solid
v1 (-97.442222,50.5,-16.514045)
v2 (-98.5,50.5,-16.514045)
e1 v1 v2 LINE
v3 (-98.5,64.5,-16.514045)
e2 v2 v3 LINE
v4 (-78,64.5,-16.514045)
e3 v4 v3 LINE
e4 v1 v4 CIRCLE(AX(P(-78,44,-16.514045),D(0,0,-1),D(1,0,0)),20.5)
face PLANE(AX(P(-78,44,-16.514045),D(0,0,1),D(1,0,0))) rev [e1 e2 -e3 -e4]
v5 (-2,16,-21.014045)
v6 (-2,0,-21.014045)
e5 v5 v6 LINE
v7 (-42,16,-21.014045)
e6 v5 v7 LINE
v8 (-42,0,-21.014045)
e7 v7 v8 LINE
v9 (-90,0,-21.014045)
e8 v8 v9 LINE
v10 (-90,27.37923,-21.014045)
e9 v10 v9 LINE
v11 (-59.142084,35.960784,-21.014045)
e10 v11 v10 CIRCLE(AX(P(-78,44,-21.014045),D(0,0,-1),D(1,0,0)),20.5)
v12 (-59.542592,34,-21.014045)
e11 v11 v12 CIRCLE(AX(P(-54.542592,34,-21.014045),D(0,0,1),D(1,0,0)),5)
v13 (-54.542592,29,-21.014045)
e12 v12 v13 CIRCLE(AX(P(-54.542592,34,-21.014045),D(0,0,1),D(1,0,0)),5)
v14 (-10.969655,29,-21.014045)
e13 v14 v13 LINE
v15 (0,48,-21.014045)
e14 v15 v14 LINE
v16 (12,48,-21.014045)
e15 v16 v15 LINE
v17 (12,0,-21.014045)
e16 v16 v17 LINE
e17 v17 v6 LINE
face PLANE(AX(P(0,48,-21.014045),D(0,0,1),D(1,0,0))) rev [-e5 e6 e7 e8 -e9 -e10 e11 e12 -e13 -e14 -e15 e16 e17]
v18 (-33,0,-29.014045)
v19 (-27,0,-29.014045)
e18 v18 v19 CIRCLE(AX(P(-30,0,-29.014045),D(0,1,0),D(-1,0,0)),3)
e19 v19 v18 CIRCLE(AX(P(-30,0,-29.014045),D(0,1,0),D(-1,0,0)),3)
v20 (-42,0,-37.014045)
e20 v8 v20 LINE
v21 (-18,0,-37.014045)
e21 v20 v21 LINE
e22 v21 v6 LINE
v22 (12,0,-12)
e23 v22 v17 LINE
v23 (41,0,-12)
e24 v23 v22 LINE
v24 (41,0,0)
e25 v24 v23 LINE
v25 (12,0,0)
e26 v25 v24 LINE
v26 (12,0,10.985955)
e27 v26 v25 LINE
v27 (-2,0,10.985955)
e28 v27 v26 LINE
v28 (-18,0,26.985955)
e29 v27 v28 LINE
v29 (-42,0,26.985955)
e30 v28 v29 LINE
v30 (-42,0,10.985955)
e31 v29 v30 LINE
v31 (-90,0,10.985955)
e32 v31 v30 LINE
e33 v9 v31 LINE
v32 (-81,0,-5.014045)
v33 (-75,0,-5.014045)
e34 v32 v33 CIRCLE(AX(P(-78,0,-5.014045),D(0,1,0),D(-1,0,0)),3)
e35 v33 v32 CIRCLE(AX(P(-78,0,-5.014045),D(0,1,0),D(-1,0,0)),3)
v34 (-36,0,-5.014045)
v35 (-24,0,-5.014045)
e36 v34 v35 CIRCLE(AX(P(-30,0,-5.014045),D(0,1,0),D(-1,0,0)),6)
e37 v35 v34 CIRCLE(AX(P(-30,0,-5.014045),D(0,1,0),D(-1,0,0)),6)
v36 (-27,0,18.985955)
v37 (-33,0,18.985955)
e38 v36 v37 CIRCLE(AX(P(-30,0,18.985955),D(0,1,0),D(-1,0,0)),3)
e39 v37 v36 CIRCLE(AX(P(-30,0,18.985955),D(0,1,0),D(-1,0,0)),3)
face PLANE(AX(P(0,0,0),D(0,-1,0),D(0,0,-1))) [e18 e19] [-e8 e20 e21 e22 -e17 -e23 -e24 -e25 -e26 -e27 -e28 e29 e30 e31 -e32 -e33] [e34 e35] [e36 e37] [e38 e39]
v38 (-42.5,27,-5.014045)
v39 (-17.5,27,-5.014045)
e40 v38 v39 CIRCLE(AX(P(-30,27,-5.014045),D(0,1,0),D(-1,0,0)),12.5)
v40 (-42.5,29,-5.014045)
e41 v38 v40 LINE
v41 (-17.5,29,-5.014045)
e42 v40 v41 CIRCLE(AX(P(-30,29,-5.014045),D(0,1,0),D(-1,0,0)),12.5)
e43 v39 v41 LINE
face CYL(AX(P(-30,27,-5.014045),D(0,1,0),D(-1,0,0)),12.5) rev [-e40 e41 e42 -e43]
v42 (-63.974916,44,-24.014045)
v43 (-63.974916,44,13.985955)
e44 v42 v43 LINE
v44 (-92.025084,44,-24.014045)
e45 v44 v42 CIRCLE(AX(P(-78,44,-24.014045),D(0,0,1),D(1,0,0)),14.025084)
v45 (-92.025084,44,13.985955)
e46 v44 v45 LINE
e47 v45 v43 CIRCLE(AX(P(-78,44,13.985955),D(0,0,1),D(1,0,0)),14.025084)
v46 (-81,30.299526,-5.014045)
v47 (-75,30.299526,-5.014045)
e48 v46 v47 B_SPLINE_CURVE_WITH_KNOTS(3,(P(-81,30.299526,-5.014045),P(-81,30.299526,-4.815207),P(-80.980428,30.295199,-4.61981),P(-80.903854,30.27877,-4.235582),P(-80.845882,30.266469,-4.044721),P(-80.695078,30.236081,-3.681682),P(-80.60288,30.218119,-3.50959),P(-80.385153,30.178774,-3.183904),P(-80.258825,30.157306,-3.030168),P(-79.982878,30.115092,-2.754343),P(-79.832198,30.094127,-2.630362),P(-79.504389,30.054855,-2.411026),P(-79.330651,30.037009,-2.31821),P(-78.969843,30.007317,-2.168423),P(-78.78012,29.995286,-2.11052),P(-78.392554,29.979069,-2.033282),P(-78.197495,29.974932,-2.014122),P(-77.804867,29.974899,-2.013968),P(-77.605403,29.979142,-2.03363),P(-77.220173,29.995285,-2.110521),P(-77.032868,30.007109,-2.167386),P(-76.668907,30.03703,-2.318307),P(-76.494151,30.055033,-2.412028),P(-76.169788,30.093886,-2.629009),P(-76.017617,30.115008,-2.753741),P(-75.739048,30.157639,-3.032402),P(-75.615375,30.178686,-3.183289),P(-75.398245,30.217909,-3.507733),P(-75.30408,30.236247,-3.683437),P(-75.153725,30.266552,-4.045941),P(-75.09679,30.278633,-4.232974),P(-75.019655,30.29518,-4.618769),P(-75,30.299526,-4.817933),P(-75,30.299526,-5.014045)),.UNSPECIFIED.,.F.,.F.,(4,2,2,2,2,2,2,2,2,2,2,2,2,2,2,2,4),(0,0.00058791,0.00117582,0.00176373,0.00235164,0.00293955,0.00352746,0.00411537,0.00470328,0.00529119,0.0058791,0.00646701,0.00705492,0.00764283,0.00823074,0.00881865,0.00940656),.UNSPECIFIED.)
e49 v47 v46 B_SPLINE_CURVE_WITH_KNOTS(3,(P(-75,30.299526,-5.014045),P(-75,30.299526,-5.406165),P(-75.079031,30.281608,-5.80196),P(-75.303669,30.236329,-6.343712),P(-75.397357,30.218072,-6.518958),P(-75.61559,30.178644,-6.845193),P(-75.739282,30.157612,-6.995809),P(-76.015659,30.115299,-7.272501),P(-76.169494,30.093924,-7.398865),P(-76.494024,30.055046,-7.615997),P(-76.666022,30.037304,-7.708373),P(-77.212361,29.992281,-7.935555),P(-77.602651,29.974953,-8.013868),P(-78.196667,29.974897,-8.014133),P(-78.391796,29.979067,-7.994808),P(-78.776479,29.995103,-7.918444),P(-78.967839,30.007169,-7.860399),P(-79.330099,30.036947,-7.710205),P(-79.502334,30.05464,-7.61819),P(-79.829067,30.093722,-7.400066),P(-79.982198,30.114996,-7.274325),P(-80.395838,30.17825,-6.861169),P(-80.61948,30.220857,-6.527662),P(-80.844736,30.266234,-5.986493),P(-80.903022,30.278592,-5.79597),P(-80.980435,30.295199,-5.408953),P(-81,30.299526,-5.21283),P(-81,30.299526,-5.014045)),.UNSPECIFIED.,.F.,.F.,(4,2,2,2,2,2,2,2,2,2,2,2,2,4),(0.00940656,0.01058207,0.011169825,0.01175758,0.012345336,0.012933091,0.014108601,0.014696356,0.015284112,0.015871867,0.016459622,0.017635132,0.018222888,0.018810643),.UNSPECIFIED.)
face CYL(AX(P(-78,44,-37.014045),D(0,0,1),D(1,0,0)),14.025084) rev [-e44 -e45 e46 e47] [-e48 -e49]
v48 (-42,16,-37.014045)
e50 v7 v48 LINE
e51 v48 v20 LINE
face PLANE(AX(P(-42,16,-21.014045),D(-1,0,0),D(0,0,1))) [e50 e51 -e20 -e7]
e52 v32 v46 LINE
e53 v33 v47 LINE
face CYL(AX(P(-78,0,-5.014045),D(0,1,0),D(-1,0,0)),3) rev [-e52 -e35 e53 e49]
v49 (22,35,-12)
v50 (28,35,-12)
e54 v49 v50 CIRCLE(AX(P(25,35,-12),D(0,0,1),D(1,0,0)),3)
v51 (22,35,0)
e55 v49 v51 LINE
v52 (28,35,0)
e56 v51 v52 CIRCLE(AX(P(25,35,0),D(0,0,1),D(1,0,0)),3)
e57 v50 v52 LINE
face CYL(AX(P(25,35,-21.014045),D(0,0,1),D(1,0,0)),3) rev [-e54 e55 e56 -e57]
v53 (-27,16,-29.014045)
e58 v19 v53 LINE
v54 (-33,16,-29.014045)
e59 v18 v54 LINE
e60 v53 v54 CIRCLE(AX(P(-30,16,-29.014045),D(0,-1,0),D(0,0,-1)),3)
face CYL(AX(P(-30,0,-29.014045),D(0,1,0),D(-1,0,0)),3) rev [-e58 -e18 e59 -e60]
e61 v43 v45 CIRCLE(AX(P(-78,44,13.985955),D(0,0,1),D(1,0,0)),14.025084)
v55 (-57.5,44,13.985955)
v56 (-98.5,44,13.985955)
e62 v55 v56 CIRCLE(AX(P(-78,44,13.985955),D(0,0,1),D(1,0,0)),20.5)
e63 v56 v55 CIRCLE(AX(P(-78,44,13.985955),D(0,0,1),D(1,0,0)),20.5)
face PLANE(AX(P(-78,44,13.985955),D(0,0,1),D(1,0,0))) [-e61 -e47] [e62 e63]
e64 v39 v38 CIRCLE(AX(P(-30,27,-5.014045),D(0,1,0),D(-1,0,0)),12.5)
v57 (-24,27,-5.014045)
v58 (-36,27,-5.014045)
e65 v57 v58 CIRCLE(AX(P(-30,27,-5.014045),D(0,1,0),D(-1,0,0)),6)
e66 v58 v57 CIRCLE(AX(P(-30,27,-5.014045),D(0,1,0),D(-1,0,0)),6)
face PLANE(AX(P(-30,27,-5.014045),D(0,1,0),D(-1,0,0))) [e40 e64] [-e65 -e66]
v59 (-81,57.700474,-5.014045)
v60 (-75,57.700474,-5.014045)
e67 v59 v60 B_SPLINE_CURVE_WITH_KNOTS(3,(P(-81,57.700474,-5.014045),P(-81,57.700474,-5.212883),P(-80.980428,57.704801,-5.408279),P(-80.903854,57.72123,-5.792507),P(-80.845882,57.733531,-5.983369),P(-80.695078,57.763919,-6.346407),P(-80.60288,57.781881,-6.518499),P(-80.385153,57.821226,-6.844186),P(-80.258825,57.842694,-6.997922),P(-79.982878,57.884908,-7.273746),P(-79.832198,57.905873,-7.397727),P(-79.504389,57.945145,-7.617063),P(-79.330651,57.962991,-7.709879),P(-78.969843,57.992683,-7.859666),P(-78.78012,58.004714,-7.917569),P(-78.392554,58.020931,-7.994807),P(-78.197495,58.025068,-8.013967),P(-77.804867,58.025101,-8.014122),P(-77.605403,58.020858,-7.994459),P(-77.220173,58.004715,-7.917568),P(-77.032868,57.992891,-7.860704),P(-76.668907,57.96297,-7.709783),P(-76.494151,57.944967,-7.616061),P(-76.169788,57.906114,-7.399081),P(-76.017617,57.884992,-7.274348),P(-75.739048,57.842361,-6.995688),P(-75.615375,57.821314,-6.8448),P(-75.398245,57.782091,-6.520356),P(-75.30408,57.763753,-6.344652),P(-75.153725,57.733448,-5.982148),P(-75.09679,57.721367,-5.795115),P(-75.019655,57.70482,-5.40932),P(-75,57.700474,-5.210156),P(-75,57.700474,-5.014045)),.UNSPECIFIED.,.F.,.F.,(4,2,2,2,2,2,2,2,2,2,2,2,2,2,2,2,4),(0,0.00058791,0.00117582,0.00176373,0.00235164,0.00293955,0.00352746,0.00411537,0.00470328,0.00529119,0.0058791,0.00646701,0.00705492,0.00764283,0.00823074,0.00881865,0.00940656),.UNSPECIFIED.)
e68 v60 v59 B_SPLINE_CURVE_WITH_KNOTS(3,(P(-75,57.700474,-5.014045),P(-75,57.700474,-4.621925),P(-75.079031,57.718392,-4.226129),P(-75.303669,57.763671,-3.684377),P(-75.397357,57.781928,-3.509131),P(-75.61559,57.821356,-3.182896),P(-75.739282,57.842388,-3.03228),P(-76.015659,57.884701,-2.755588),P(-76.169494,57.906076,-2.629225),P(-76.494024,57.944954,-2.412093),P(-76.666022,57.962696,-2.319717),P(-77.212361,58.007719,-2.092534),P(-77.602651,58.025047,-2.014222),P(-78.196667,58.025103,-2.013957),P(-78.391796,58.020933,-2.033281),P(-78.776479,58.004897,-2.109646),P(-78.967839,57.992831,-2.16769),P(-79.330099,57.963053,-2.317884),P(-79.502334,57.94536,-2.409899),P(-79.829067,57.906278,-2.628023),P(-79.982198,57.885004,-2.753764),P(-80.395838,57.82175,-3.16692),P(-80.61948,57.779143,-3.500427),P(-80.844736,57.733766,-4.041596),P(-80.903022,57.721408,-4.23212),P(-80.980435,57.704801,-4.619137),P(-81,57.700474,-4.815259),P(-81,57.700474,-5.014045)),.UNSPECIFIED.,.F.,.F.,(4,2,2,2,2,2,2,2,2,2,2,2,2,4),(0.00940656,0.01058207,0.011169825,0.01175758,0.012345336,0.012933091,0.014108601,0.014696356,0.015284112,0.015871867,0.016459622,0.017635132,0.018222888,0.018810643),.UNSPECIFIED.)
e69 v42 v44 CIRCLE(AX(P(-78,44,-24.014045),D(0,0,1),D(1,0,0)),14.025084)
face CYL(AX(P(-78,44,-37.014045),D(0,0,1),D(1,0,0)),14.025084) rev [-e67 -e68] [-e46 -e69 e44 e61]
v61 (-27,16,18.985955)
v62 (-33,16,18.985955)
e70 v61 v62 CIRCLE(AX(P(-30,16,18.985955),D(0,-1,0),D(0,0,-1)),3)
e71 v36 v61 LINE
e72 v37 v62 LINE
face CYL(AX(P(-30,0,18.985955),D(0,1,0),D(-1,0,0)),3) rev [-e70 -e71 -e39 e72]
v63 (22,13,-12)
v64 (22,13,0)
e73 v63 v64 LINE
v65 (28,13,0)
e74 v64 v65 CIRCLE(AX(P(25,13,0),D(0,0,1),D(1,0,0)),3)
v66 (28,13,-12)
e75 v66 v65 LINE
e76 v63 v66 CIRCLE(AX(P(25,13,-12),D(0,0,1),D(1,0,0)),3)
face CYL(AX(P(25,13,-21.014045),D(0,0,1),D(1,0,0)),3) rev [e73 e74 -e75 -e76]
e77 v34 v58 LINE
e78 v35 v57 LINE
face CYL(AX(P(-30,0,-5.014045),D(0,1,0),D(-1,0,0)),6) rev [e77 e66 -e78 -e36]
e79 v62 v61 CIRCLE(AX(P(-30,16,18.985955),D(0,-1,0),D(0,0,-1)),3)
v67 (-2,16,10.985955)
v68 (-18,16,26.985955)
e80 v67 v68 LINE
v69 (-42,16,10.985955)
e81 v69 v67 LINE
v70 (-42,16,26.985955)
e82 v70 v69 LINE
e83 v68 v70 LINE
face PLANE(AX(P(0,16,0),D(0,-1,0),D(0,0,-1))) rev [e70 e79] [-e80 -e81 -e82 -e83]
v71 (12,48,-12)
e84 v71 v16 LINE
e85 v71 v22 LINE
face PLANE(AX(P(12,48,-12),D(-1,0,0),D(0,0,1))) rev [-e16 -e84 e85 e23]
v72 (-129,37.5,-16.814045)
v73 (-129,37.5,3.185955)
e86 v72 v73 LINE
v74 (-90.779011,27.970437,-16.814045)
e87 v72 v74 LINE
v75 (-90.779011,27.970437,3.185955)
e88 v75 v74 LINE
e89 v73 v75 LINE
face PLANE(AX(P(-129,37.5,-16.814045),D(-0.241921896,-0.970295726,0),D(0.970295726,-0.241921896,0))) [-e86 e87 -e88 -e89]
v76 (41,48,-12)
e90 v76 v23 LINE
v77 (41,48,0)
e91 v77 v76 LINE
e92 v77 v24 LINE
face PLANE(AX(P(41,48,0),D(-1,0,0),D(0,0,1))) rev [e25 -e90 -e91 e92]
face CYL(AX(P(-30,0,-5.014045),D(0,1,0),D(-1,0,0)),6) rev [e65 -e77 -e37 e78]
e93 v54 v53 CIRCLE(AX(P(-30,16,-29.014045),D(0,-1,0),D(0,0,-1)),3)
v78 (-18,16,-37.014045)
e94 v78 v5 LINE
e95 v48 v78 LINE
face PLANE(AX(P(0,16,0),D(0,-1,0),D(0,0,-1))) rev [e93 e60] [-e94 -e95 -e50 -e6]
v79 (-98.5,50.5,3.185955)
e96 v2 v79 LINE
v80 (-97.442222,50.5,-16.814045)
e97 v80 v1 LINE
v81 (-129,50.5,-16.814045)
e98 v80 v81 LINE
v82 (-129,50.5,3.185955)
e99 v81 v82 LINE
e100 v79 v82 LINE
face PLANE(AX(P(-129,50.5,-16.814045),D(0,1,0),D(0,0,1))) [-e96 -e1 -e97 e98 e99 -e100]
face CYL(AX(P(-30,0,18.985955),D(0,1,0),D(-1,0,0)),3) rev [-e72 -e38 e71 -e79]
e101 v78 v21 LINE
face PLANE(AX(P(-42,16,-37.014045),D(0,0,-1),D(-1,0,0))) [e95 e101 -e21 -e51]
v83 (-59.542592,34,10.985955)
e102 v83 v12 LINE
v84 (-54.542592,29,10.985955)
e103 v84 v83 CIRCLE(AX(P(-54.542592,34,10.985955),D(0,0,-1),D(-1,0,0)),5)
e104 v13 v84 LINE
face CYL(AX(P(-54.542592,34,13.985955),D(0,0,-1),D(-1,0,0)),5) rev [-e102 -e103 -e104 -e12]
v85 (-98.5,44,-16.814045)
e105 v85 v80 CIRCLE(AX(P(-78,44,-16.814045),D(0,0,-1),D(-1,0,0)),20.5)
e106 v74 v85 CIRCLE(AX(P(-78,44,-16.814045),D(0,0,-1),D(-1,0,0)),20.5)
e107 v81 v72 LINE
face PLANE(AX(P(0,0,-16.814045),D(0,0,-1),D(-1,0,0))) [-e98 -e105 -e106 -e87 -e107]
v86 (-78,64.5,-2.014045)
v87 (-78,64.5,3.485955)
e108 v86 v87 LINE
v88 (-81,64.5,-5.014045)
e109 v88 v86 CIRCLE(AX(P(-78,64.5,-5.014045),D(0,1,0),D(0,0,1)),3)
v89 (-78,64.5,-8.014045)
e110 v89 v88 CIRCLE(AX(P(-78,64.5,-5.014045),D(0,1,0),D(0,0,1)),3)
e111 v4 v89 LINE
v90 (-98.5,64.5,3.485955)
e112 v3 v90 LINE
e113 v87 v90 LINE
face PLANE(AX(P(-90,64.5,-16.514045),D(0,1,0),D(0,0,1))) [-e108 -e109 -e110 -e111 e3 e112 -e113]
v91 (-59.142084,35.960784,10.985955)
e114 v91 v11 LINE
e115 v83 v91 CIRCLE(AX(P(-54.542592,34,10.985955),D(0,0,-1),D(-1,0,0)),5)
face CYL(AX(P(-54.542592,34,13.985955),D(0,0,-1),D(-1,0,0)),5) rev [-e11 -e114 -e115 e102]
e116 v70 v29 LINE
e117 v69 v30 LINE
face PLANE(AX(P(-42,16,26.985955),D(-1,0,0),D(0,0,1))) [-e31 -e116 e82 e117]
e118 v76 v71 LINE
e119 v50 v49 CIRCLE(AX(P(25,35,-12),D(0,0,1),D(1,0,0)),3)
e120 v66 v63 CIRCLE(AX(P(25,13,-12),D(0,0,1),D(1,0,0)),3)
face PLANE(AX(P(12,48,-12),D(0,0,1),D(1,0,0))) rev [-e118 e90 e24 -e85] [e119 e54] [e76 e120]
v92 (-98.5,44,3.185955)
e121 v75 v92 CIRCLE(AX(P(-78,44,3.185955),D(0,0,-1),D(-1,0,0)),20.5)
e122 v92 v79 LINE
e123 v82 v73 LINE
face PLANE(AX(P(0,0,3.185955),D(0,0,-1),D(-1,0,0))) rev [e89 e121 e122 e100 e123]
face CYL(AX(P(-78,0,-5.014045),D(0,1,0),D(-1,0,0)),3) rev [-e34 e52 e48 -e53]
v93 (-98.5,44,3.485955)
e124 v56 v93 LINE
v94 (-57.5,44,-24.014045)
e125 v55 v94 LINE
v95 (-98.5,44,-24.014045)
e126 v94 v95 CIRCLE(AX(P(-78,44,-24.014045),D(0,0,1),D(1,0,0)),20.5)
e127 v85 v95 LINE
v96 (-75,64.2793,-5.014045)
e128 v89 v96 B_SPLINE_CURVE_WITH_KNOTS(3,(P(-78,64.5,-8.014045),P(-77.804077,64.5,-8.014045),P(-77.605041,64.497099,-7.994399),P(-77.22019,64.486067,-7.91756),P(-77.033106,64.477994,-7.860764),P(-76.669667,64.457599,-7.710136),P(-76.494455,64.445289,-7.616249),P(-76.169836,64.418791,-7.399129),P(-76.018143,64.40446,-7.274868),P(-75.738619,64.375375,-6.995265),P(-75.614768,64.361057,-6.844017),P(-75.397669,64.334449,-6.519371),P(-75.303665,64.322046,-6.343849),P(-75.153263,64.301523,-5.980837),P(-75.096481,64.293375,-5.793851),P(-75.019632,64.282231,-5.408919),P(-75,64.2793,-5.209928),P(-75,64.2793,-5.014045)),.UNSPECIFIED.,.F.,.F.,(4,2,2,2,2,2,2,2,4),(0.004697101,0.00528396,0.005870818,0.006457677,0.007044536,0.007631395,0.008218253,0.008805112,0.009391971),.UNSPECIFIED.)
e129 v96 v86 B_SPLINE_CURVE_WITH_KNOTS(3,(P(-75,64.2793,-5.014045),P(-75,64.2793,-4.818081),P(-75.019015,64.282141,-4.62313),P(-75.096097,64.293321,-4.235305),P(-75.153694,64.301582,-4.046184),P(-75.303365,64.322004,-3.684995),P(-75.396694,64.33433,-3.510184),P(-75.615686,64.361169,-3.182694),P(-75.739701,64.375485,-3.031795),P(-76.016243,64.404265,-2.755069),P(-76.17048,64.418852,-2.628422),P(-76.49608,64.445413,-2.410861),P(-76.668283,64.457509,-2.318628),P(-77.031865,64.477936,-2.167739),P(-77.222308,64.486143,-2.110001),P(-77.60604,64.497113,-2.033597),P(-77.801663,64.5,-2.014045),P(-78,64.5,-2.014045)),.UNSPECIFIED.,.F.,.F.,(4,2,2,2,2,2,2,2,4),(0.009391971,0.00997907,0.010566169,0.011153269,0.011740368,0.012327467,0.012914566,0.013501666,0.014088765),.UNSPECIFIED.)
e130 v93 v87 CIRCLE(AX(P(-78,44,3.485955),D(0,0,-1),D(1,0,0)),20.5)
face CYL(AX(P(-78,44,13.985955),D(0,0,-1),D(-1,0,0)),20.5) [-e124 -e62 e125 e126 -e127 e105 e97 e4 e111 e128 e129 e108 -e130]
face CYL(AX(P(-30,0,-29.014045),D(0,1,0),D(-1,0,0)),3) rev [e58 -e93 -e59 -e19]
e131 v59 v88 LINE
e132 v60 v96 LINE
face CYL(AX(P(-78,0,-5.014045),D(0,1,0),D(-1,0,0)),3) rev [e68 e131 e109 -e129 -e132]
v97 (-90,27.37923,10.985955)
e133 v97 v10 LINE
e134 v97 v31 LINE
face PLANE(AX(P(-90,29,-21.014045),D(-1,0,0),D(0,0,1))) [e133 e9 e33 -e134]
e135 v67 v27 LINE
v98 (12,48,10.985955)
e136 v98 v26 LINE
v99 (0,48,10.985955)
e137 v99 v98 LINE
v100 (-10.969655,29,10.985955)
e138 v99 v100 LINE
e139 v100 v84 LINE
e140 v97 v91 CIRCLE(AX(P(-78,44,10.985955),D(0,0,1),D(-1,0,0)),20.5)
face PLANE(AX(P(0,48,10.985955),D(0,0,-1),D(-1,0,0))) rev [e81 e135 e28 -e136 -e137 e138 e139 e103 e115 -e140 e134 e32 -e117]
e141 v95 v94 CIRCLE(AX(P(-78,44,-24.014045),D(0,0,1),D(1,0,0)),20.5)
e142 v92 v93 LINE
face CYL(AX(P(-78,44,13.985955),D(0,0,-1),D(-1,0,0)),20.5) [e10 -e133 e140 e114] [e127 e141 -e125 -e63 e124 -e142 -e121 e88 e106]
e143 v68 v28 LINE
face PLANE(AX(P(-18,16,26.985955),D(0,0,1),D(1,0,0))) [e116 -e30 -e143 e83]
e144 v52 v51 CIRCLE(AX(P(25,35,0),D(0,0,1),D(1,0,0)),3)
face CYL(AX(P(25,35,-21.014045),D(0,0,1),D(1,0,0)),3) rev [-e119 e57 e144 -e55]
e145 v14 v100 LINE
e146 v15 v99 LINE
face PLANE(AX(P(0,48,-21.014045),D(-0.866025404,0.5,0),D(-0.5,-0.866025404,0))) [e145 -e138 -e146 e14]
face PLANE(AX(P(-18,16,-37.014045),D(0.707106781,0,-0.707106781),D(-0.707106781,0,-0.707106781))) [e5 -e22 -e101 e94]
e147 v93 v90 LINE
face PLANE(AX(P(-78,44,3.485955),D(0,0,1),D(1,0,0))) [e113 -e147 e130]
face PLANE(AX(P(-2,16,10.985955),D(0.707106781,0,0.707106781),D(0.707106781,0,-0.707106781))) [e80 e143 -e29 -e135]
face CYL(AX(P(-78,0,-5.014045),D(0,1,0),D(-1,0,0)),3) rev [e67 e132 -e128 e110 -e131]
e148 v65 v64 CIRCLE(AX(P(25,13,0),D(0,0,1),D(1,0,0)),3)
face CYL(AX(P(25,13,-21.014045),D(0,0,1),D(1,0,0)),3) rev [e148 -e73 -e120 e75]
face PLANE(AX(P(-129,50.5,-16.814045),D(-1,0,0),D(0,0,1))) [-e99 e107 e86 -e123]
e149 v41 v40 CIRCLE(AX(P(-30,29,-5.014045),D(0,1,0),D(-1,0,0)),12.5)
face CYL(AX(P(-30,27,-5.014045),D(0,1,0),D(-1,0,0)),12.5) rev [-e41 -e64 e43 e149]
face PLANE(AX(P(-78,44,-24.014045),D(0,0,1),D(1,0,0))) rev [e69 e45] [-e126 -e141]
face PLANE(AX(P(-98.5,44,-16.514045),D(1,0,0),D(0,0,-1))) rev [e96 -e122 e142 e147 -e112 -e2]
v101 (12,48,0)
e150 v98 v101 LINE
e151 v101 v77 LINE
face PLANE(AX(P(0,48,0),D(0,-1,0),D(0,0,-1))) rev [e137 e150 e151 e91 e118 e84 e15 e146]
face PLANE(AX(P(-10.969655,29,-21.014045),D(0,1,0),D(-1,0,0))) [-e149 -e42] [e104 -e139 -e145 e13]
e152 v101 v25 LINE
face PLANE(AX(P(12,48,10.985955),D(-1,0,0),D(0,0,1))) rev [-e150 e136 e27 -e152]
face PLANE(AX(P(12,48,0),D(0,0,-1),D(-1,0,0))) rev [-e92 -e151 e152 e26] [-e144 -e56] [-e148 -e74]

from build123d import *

# Parameters (mm, degrees)
BASE_BLOCK_48MM_DEPTH      = 48
BASE_NOTCH_SKETCH_R        = 3
BASE_NOTCH_CUT_DEPTH       = 67.532624112
ANGLED_ARM_30DEG_DEPTH     = 32
MOUNTING_FLANGE_DEPTH      = 3
MOUNTING_FLANGE_DEPTH_BACK = 35
MOUNTING_FLANGE_SKETCH_R   = 20.5
MOUNTING_FLANGE_SKETCH_R_2 = 14
RAISED_BLOCK_16MM_DEPTH    = 16
POCKET_SKETCH_R            = 3.17708526
POCKET_SKETCH_R_2          = 3.631937334
POCKET_SKETCH_R_3          = 12.5
POCKET_CUT_2MM_DEPTH       = 2
SLOT_SKETCH_R              = 6
SLOT_SKETCH_R_2            = 3
SLOT_CUT_DEPTH             = 112.707383368
CHANNEL_CUT_DEPTH          = 112.05196756
CHANNEL_CUT_DEPTH_BACK     = 112.05196756
CHANNEL_SKETCH_R           = 3
LUG_START                  = -27.5
LUG_A_DEPTH                = 20
LUG_B_DEPTH                = 20
LUG_START_2                = -10.8
LUG_C_DEPTH                = 20
FLANGE_HOLE_DEPTH          = 153.977939634
FLANGE_HOLE_DEPTH_BACK     = 153.977939634
FLANGE_HOLE_SKETCH_R       = 14.02508448
LUG_A_HOLE_DEPTH           = 149.900266997
LUG_A_HOLE_DEPTH_BACK      = 149.900266997
LUG_A_HOLE_SKETCH_R        = 3
ARM_FILLET_R5_R            = 5


with BuildPart() as part:
    # Base Block Sketch → Base Block 48mm (new body)
    with BuildSketch(Plane(origin=(0, 0, 0), x_dir=(1, 0, 0), z_dir=(0, 1, 0))):
        Polygon((12, 0), (41, 0), (41, 12), (12, 12), (12, 21.014044617), (0, 21.014044617), (0, -10.985955383), (12, -10.985955383), align=None)
    extrude(amount=BASE_BLOCK_48MM_DEPTH)

    # Base Notch Sketch → Base Notch Cut (cut, through all)
    with BuildSketch(Plane.XY):
        with Locations((25, 35)):
            Circle(BASE_NOTCH_SKETCH_R)
        with Locations((25, 13)):
            Circle(BASE_NOTCH_SKETCH_R)
    extrude(amount=-BASE_NOTCH_CUT_DEPTH, mode=Mode.SUBTRACT)

    # Angled Arm Sketch → Angled Arm 30deg (add)
    with BuildSketch(Plane.XY.offset(10.985955383)):
        Polygon((0, 48), (-10.969655115, 29), (-90, 29), (-90, 0), (0, 0), align=None)
    extrude(amount=-ANGLED_ARM_30DEG_DEPTH)

    # Mounting Flange Sketch → Mounting Flange (add, two sides: drawn at the far end of the back side and taken through both)
    with BuildSketch(Plane.XY.offset(10.985955383).offset(-MOUNTING_FLANGE_DEPTH_BACK)):
        with Locations((-78, 44)):
            Circle(MOUNTING_FLANGE_SKETCH_R)
        with Locations((-78, 44)):
            Circle(MOUNTING_FLANGE_SKETCH_R_2, mode=Mode.SUBTRACT)
    extrude(amount=MOUNTING_FLANGE_DEPTH + MOUNTING_FLANGE_DEPTH_BACK)

    # Raised Block Sketch → Raised Block 16mm (add)
    with BuildSketch(Plane.XZ):
        Polygon((-42, -37.014044617), (-18, -37.014044617), (-2, -21.014044617), (-42, -21.014044617), align=None)
        Polygon((-42, 10.985955383), (-2, 10.985955383), (-18, 26.985955383), (-42, 26.985955383), align=None)
    extrude(amount=-RAISED_BLOCK_16MM_DEPTH)

    # Pocket Sketch → Pocket Cut 2mm (cut)
    with BuildSketch(Plane(origin=(0, 29, 0), x_dir=(1, 0, 0), z_dir=(0, 1, 0))):
        with Locations((-30, -18.985955383)):
            Circle(POCKET_SKETCH_R)
        with Locations((-30, 29.014044617)):
            Circle(POCKET_SKETCH_R_2)
        with Locations(Location((-30, 5.014044617, 0), (0, 0, 180))):
            Circle(POCKET_SKETCH_R_3)
    extrude(amount=-POCKET_CUT_2MM_DEPTH, mode=Mode.SUBTRACT)

    # Slot Sketch → Slot Cut (cut, through all)
    with BuildSketch(Plane(origin=(0, 27, 0), x_dir=(1, 0, 0), z_dir=(0, 1, 0))):
        with Locations(Location((-30, 5.014044617, 0), (0, 0, 180))):
            Circle(SLOT_SKETCH_R)
        with Locations(Location((-30, -18.985955383, 0), (0, 0, 180))):
            Circle(SLOT_SKETCH_R_2)
        with Locations(Location((-30, 29.014044617, 0), (0, 0, 180))):
            Circle(SLOT_SKETCH_R_2)
    extrude(amount=-SLOT_CUT_DEPTH, mode=Mode.SUBTRACT)

    # Channel Sketch → Channel Cut (cut, two sides: drawn at the far end of the back side and taken through both)
    with BuildSketch(Plane(origin=(0, 29, 0), x_dir=(1, 0, 0), z_dir=(0, 1, 0)).offset(-CHANNEL_CUT_DEPTH_BACK)):
        with Locations(Location((-78, 5.014044617, 0), (0, 0, 180))):
            Circle(CHANNEL_SKETCH_R)
    extrude(amount=CHANNEL_CUT_DEPTH + CHANNEL_CUT_DEPTH_BACK, mode=Mode.SUBTRACT)

    # Lug A Sketch → Lug A (add)
    with BuildSketch(Plane.XY.offset(10.985955383).offset(LUG_START)):
        with BuildLine():
            Line((-90, 64.5), (-78, 64.5))
            ThreePointArc((-78, 64.5), (-84.305720108, 63.50609889), (-90, 60.620770139))
            Line((-90, 60.620770139), (-90, 64.5))
        make_face()
    extrude(amount=LUG_A_DEPTH)

    # Lug B Sketch → Lug B (add)
    with BuildSketch(Plane.XY.offset(10.985955383).offset(LUG_START)):
        with BuildLine():
            Line((-98.5, 44), (-98.5, 64.5))
            Line((-98.5, 64.5), (-90, 64.5))
            Line((-90, 64.5), (-90, 60.620770139))
            ThreePointArc((-90, 60.620770139), (-96.251712248, 53.334077351), (-98.5, 44))
        make_face()
    extrude(amount=LUG_B_DEPTH)

    # Lug C Sketch → Lug C (add)
    with BuildSketch(Plane.XY.offset(13.985955383).offset(LUG_START_2)):
        Polygon((-129, 50.5), (-129, 37.5), (-90, 27.776207889), (-90, 50.5), align=None)
    extrude(amount=-LUG_C_DEPTH)

    # Flange Hole Sketch → Flange Hole (cut, two sides: drawn at the far end of the back side and taken through both)
    with BuildSketch(Plane.XY.offset(13.985955383).offset(-FLANGE_HOLE_DEPTH_BACK)):
        with Locations((-78, 44)):
            Circle(FLANGE_HOLE_SKETCH_R)
    extrude(amount=FLANGE_HOLE_DEPTH + FLANGE_HOLE_DEPTH_BACK, mode=Mode.SUBTRACT)

    # Lug A Hole Sketch → Lug A Hole (cut, two sides: drawn at the far end of the back side and taken through both)
    with BuildSketch(Plane(origin=(0, 64.5, 0), x_dir=(1, 0, 0), z_dir=(0, 1, 0)).offset(-LUG_A_HOLE_DEPTH_BACK)):
        with Locations(Location((-78, 5.014044617, 0), (0, 0, 180))):
            Circle(LUG_A_HOLE_SKETCH_R)
    extrude(amount=LUG_A_HOLE_DEPTH + LUG_A_HOLE_DEPTH_BACK, mode=Mode.SUBTRACT)

    # Arm Fillet R5
    arm_fillet_r5_edges = [part.edges().sort_by_distance(p)[0] for p in [
        (-64.026811388, 29, -5.014044617),
    ]]
    fillet(arm_fillet_r5_edges, radius=ARM_FILLET_R5_R)


solid = part.part
